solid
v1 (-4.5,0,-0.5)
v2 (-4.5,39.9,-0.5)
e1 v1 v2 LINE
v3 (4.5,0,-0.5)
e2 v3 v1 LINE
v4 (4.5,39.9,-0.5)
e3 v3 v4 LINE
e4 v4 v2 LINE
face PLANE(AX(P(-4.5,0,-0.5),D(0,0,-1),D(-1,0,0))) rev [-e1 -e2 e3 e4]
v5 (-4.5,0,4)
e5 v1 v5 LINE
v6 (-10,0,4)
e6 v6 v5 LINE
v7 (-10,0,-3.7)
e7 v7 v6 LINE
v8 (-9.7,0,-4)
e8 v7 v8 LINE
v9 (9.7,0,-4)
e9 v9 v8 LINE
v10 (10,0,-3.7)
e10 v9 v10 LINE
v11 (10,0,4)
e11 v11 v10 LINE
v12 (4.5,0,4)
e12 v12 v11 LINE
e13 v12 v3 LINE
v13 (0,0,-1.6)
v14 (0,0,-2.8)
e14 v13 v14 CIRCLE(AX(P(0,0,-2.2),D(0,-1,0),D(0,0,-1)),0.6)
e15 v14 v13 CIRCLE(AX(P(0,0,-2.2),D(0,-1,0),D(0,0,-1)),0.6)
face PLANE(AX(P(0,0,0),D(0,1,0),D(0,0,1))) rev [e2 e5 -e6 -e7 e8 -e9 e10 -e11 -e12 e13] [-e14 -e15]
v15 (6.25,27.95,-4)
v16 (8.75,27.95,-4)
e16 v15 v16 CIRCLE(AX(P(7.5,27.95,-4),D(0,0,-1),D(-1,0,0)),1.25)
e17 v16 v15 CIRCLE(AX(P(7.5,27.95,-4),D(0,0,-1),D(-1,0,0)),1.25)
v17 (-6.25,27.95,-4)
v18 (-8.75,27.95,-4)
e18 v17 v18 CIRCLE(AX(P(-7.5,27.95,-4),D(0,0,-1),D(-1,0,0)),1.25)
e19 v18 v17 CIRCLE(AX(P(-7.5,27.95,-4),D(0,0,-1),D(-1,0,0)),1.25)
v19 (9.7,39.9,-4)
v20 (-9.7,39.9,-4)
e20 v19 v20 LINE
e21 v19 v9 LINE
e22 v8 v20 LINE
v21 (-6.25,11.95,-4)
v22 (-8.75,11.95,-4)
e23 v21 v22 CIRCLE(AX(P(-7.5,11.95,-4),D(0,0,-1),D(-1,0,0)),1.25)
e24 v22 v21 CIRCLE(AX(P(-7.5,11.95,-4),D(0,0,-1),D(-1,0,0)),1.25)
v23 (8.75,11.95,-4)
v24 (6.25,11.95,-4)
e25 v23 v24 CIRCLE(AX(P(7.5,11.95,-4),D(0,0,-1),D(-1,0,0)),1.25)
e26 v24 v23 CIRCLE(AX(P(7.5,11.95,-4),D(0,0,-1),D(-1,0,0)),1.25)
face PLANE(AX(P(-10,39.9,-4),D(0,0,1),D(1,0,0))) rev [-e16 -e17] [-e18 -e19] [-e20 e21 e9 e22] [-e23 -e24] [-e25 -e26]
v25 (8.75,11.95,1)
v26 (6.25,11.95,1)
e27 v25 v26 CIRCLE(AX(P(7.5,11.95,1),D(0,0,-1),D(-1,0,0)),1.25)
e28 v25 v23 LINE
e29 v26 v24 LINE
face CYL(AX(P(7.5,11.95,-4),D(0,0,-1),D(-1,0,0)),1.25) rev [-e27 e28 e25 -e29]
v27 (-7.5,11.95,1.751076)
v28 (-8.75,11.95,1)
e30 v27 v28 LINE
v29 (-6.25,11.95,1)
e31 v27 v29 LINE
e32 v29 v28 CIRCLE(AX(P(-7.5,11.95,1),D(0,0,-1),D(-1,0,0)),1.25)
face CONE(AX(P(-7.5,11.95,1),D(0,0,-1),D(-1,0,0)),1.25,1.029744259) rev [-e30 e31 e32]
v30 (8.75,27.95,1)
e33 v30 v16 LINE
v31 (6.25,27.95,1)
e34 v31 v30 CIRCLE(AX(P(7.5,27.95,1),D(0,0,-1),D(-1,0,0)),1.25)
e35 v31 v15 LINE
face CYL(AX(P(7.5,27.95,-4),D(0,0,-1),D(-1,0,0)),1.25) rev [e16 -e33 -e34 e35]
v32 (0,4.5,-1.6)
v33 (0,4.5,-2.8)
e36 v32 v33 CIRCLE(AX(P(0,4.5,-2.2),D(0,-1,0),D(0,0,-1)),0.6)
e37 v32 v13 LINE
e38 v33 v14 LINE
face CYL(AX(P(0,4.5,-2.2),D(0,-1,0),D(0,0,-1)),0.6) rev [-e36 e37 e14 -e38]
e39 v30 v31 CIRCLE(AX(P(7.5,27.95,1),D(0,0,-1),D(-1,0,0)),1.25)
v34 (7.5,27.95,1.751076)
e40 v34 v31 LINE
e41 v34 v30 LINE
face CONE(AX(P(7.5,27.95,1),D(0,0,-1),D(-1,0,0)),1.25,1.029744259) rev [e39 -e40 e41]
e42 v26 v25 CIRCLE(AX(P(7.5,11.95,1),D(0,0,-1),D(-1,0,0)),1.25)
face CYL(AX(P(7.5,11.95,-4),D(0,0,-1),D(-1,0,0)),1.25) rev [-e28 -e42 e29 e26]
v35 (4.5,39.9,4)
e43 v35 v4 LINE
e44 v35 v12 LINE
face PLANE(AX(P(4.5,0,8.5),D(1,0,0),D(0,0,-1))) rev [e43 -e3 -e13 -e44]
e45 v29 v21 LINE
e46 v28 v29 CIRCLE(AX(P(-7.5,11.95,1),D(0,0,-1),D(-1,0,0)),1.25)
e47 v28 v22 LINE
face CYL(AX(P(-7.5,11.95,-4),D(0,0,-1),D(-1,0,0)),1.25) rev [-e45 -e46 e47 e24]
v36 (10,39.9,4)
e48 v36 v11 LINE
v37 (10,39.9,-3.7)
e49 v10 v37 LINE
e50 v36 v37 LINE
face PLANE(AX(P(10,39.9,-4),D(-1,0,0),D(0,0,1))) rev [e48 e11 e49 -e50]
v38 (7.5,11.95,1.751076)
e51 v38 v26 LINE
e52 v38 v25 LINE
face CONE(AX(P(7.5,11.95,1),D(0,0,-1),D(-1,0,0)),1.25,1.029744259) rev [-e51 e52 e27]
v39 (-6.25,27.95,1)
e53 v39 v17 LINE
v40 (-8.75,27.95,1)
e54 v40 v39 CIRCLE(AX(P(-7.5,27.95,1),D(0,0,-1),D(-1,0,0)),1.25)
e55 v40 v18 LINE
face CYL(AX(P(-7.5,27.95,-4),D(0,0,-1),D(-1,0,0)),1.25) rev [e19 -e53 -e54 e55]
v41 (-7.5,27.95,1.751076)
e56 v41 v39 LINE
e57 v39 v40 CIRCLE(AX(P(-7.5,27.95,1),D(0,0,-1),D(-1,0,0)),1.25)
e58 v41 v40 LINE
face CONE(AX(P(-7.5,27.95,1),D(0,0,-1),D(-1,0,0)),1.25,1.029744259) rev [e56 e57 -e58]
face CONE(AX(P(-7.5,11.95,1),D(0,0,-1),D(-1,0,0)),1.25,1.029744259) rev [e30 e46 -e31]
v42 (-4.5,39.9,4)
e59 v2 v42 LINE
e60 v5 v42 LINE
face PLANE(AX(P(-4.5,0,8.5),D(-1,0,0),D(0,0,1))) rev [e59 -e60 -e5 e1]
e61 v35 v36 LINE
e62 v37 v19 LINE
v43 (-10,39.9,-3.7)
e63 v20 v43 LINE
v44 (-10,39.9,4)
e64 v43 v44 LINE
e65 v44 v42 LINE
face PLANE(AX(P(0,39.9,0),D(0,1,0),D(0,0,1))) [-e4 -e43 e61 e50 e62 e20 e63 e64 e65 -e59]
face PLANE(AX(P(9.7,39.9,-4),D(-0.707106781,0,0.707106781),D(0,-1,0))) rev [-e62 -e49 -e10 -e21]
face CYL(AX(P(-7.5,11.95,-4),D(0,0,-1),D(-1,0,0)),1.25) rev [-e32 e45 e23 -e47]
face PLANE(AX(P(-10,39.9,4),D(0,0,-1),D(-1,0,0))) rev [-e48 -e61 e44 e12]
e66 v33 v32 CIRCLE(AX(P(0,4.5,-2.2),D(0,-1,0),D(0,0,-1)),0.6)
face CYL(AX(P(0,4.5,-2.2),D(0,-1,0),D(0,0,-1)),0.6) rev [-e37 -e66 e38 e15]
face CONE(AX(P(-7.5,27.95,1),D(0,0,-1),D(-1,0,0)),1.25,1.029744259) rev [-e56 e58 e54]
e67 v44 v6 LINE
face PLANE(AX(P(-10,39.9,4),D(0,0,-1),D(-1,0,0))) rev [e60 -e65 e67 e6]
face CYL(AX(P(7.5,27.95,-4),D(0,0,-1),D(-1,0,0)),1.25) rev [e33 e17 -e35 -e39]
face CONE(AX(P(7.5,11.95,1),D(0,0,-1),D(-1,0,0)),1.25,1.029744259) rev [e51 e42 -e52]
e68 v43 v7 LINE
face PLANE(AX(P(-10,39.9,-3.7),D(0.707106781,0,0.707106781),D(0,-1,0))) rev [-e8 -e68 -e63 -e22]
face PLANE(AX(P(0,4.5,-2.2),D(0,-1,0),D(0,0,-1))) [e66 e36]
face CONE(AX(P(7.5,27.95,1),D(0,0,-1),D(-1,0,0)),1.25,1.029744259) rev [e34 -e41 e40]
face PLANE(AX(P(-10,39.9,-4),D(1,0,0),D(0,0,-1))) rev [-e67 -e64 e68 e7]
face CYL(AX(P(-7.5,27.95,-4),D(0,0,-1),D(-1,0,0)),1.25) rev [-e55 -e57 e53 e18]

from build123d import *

# Parameters (mm, degrees)
SKETCH1_W             = 20
SKETCH1_H             = 8
BOSS_EXTRUDE1_DEPTH   = 39.9
SKETCH2_W             = 9
SKETCH2_H             = 9
CUT_EXTRUDE1_DEPTH    = 42.328077623
CHAMFER1_SIZE         = 0.3
SKETCH3_R             = 0.5930201
CUT_EXTRUDE2_DEPTH    = 3
SKETCH4_R             = 0.6
CUT_EXTRUDE3_DEPTH    = 4.5
M3_TAPPED_HOLE1_D     = 2.5
M3_TAPPED_HOLE1_DEPTH = 5
M3_TAPPED_HOLE1_TIP   = 0.751075774


with BuildPart() as part:
    # Sketch1 → Boss-Extrude1 (new body)
    with BuildSketch(Plane(origin=(0, 0, 0), x_dir=(1, 0, 0), z_dir=(0, 1, 0))):
        Rectangle(SKETCH1_W, SKETCH1_H)
    extrude(amount=BOSS_EXTRUDE1_DEPTH)

    # Sketch2 → Cut-Extrude1 (cut, through all)
    with BuildSketch(Plane(origin=(0, 39.9, 0), x_dir=(1, 0, 0), z_dir=(0, 1, 0))):
        with Locations((0, -4)):
            Rectangle(SKETCH2_W, SKETCH2_H)
    extrude(amount=-CUT_EXTRUDE1_DEPTH, mode=Mode.SUBTRACT)

    # Chamfer1
    chamfer1_edges = [part.edges().sort_by_distance(p)[0] for p in [
        (-10, 19.95, -4),
        (10, 19.95, -4),
    ]]
    chamfer(chamfer1_edges, length=CHAMFER1_SIZE)

    # Sketch3 → Cut-Extrude2 (cut)
    with BuildSketch(Plane(origin=(0, 0, -4), x_dir=(-1, 0, 0), z_dir=(0, 0, -1))):
        with Locations((-7.5, 27.95)):
            Circle(SKETCH3_R)
        with Locations(Location((7.5, 27.95, 0), (0, 0, 180))):
            Circle(SKETCH3_R)
        with Locations((7.5, 11.95)):
            Circle(SKETCH3_R)
        with Locations(Location((-7.5, 11.95, 0), (0, 0, 180))):
            Circle(SKETCH3_R)
    extrude(amount=-CUT_EXTRUDE2_DEPTH, mode=Mode.SUBTRACT)

    # Sketch4 → Cut-Extrude3 (cut)
    with BuildSketch(Plane.XZ):
        with Locations(Location((0, -2.2, 0), (0, 0, 270))):
            Circle(SKETCH4_R)
    extrude(amount=-CUT_EXTRUDE3_DEPTH, mode=Mode.SUBTRACT)

    # M3 Tapped Hole1
    with Locations(Plane(origin=(7.5, 11.95, -4), x_dir=(-1, 0, 0), z_dir=(0, 0, -1))):
        with Locations((0, 0), (15, 0), (15, 16), (0, 16)):
            Hole(M3_TAPPED_HOLE1_D / 2, depth=M3_TAPPED_HOLE1_DEPTH)
            with Locations((0, 0, -(M3_TAPPED_HOLE1_DEPTH + M3_TAPPED_HOLE1_TIP / 2))):  # 118° drill point
                Cone(0, M3_TAPPED_HOLE1_D / 2, M3_TAPPED_HOLE1_TIP, mode=Mode.SUBTRACT)


solid = part.part
